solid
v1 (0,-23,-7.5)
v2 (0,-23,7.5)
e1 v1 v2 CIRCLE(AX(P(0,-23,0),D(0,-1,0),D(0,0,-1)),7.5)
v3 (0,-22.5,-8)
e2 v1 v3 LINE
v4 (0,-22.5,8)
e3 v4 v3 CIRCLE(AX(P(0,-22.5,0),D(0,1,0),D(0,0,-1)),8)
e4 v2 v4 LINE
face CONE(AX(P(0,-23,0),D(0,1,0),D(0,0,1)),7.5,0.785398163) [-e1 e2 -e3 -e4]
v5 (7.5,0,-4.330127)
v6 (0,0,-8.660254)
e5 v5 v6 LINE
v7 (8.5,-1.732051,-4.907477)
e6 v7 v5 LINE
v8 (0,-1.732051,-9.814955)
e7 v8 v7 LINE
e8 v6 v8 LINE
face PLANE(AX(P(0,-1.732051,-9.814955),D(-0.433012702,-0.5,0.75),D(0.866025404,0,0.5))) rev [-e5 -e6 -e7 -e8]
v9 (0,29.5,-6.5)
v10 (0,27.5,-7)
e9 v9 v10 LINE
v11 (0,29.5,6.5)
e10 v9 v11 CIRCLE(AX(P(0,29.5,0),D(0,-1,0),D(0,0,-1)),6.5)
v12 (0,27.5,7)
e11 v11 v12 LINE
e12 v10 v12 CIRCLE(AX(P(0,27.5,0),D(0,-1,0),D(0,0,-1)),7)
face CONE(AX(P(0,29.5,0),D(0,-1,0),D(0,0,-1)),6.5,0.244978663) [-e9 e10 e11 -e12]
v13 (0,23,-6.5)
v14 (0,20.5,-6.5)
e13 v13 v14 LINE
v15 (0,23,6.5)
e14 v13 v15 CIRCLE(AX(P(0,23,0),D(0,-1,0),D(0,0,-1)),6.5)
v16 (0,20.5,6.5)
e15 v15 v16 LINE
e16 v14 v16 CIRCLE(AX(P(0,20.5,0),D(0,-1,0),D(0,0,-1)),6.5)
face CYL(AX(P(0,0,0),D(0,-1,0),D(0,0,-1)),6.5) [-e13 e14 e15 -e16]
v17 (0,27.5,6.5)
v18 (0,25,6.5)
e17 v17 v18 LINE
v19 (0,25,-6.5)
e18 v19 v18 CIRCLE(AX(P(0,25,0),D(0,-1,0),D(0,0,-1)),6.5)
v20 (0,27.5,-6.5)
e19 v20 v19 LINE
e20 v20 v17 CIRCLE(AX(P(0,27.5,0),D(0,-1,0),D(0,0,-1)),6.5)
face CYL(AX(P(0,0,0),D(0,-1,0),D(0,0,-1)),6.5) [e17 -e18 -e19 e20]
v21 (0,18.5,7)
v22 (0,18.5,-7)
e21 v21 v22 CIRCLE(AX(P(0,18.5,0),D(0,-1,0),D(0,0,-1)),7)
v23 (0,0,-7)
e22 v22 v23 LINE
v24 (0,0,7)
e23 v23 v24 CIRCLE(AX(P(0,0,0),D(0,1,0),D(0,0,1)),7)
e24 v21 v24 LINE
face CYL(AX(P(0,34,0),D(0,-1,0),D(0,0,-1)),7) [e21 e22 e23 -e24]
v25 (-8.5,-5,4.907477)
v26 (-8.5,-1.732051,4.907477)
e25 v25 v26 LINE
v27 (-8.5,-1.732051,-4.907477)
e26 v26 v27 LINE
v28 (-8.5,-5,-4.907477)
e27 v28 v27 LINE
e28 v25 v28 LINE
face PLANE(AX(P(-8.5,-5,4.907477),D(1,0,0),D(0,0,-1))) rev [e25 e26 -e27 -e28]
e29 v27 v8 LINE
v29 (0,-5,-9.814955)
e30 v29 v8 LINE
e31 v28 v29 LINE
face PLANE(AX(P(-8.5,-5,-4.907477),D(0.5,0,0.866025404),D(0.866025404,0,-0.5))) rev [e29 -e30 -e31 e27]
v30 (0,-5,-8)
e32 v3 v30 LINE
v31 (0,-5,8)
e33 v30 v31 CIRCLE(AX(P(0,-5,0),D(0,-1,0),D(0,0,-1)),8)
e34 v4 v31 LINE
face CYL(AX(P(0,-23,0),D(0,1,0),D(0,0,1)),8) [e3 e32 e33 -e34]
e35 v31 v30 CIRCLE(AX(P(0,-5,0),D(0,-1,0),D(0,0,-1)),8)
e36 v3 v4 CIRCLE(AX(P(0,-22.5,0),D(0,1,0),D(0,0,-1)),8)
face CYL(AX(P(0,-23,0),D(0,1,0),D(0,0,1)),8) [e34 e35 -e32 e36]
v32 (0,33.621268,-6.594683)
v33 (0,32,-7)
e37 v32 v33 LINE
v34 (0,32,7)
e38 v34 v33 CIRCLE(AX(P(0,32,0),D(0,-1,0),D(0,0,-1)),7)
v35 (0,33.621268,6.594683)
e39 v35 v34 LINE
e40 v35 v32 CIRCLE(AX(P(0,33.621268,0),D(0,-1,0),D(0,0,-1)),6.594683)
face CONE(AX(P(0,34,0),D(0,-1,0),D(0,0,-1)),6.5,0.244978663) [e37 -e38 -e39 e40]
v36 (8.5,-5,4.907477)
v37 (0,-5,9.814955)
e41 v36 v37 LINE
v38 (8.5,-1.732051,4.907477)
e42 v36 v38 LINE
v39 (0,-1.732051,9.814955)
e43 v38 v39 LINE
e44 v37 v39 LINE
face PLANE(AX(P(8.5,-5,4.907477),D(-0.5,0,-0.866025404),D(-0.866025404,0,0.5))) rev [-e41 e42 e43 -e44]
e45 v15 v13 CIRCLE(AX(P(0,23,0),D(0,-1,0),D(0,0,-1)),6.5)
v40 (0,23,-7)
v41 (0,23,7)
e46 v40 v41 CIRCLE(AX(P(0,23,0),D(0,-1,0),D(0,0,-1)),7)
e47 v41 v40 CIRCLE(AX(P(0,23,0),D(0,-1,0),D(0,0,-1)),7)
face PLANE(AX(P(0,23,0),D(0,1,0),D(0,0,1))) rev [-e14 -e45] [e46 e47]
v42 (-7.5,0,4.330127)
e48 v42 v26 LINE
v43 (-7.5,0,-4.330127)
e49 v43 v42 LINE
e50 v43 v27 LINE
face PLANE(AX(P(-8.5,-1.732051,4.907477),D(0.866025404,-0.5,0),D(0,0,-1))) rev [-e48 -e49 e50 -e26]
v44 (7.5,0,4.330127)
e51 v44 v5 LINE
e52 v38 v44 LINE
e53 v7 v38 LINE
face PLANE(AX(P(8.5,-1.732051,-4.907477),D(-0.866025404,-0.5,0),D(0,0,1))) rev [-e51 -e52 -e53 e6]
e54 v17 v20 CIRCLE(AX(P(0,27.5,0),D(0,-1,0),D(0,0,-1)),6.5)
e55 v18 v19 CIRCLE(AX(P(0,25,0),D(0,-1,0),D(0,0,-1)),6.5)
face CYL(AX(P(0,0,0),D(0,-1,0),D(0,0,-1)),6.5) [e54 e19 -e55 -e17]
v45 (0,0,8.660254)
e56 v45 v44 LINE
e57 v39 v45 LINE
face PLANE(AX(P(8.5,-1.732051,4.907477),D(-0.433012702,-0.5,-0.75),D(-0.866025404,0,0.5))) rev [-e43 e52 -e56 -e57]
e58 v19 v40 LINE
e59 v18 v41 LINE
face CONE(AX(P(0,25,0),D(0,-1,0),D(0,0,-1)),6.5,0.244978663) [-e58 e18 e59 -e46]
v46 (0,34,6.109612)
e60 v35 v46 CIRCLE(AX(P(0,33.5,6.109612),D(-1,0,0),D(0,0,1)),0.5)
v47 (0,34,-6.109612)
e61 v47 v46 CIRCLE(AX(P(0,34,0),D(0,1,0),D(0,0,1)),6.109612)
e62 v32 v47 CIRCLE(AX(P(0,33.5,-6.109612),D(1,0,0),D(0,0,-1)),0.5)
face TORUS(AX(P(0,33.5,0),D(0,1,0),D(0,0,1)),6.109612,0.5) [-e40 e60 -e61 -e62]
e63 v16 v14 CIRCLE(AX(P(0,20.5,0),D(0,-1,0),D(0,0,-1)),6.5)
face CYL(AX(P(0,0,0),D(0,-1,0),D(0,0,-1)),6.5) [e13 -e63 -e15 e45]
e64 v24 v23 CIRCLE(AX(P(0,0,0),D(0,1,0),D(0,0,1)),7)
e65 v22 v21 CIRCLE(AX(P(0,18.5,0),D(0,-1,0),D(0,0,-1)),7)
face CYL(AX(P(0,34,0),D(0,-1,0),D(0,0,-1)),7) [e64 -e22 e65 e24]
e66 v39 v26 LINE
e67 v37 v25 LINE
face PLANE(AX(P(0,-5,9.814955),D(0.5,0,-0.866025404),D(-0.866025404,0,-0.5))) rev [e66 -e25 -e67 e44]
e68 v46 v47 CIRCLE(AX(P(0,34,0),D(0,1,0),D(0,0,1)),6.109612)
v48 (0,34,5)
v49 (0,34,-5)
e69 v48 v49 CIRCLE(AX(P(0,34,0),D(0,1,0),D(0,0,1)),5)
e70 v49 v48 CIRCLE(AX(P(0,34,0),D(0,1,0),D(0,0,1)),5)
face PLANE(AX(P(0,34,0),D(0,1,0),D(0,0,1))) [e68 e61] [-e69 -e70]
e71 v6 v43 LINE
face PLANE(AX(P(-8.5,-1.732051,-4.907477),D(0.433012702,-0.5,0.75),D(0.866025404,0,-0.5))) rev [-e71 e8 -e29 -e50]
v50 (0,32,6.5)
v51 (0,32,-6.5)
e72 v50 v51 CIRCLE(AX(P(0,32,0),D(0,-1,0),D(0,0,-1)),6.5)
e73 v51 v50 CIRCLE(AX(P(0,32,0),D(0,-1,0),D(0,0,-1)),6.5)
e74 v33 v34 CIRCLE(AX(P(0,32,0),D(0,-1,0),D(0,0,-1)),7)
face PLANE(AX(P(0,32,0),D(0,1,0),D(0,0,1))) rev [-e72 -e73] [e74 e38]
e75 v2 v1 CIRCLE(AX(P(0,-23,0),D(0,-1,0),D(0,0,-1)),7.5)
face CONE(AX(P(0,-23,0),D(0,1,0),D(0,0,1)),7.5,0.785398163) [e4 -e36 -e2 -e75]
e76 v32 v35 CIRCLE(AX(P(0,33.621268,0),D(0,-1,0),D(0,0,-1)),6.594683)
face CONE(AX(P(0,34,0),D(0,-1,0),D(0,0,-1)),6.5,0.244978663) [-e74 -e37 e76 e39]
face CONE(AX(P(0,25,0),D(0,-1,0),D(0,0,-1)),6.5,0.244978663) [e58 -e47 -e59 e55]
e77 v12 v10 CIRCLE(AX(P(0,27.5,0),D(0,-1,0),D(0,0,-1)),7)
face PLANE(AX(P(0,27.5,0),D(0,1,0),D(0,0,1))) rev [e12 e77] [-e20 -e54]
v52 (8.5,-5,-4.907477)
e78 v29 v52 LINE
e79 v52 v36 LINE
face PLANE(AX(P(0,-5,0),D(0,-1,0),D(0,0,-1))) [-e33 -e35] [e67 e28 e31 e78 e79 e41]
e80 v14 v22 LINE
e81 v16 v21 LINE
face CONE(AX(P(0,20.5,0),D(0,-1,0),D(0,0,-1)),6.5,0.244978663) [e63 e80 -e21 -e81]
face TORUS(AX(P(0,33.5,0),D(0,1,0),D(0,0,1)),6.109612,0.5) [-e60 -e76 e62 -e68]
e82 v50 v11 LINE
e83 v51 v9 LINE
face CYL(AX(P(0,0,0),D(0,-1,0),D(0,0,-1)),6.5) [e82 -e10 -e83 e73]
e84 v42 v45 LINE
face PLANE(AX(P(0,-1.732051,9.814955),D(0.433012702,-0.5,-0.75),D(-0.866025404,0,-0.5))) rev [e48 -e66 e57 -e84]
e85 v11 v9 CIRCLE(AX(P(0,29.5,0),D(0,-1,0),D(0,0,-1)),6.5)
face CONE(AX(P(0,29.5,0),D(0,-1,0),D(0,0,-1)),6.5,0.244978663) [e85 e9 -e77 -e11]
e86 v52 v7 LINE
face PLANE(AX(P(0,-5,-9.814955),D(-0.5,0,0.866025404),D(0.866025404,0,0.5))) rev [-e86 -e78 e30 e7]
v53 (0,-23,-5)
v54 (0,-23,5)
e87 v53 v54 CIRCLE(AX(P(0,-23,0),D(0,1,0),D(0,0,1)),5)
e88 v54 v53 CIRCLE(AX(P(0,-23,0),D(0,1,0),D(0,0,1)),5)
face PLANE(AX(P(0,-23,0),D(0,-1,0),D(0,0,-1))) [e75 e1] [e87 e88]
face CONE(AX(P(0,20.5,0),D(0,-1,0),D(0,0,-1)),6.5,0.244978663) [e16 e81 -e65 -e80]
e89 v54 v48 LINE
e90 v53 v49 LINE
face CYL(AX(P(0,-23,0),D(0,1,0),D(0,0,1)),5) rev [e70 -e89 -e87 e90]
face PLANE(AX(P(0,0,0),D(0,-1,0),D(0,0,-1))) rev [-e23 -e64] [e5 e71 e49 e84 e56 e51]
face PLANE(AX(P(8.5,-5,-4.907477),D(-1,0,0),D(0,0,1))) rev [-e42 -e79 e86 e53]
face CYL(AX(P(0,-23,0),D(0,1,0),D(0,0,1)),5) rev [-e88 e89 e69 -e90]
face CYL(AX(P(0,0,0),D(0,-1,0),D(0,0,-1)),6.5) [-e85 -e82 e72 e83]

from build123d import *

# Parameters (mm, degrees)
SKETCH2_R           = 7
BOSS_EXTRUDE1_DEPTH = 34
BOSS_EXTRUDE2_DEPTH = 5
SKETCH6_R           = 8
BOSS_EXTRUDE3_DEPTH = 18
SKETCH4_R           = 5
CUT_EXTRUDE1_DEPTH  = 59.460100353
CHAMFER1_SIZE       = 1
CHAMFER1_SIZE2      = 1.732050808
CHAMFER3_SIZE       = 0.5
FILLET1_R           = 0.5


with BuildPart() as part:
    # Sketch2 → Boss-Extrude1 (new body)
    with BuildSketch(Plane(origin=(0, 0, 0), x_dir=(1, 0, 0), z_dir=(0, 1, 0))):
        with Locations(Location((0, 0, 0), (0, 0, 270))):
            Circle(SKETCH2_R)
    extrude(amount=BOSS_EXTRUDE1_DEPTH)

    # Sketch3 → Cut-Revolve1 (revolve, cut)
    with BuildSketch(Plane.XY, mode=Mode.PRIVATE) as cut_revolve1_sk:
        Polygon((6.5, 34), (7, 32), (6.5, 32), (6.5, 29.5), (7, 27.5), (6.5, 27.5), (6.5, 25), (7, 23), (6.5, 23), (6.5, 20.5), (7, 18.5), (7, 34), align=None)
    revolve(cut_revolve1_sk.sketch.rotate(Axis((0, 0, 0), (0, 1, 0)), 90), axis=Axis((0, 0, 0), (0, 1, 0)), mode=Mode.SUBTRACT)

    # Sketch5 → Boss-Extrude2 (add)
    with BuildSketch(Plane.XZ):
        Polygon((8.5, -4.907477288), (8.5, 4.907477288), (0, 9.814954576), (-8.5, 4.907477288), (-8.5, -4.907477288), (0, -9.814954576), align=None)
    extrude(amount=BOSS_EXTRUDE2_DEPTH)

    # Sketch6 → Boss-Extrude3 (add)
    with BuildSketch(Plane.XZ.offset(5)):
        with Locations(Location((0, 0, 0), (0, 0, 270))):
            Circle(SKETCH6_R)
    extrude(amount=BOSS_EXTRUDE3_DEPTH)

    # Sketch4 → Cut-Extrude1 (cut, through all)
    with BuildSketch(Plane(origin=(0, 34, 0), x_dir=(1, 0, 0), z_dir=(0, 1, 0))):
        with Locations(Location((0, 0, 0), (0, 0, 270))):
            Circle(SKETCH4_R)
    extrude(amount=-CUT_EXTRUDE1_DEPTH, mode=Mode.SUBTRACT)

    # Chamfer1
    chamfer1_edges = [part.edges().sort_by_distance(p)[0] for p in [
        (4.25, 0, -7.361215932),
        (8.5, 0, 0),
        (4.25, 0, 7.361215932),
        (-4.25, 0, 7.361215932),
        (-8.5, 0, 0),
        (-4.25, 0, -7.361215932),
    ]]
    chamfer1_side = [part.faces().sort_by_distance(p)[0] for p in [
        (8.240320711, 0, 0),
    ]]
    chamfer(chamfer1_edges, length=CHAMFER1_SIZE, length2=CHAMFER1_SIZE2, reference=chamfer1_side[0])

    # Chamfer3
    chamfer3_edges = [part.edges().sort_by_distance(p)[0] for p in [
        (0, -23, 8),
    ]]
    chamfer(chamfer3_edges, length=CHAMFER3_SIZE)

    # Fillet1
    fillet1_edges = [part.edges().sort_by_distance(p)[0] for p in [
        (0, 34, 6.5),
    ]]
    fillet(fillet1_edges, radius=FILLET1_R)


solid = part.part
